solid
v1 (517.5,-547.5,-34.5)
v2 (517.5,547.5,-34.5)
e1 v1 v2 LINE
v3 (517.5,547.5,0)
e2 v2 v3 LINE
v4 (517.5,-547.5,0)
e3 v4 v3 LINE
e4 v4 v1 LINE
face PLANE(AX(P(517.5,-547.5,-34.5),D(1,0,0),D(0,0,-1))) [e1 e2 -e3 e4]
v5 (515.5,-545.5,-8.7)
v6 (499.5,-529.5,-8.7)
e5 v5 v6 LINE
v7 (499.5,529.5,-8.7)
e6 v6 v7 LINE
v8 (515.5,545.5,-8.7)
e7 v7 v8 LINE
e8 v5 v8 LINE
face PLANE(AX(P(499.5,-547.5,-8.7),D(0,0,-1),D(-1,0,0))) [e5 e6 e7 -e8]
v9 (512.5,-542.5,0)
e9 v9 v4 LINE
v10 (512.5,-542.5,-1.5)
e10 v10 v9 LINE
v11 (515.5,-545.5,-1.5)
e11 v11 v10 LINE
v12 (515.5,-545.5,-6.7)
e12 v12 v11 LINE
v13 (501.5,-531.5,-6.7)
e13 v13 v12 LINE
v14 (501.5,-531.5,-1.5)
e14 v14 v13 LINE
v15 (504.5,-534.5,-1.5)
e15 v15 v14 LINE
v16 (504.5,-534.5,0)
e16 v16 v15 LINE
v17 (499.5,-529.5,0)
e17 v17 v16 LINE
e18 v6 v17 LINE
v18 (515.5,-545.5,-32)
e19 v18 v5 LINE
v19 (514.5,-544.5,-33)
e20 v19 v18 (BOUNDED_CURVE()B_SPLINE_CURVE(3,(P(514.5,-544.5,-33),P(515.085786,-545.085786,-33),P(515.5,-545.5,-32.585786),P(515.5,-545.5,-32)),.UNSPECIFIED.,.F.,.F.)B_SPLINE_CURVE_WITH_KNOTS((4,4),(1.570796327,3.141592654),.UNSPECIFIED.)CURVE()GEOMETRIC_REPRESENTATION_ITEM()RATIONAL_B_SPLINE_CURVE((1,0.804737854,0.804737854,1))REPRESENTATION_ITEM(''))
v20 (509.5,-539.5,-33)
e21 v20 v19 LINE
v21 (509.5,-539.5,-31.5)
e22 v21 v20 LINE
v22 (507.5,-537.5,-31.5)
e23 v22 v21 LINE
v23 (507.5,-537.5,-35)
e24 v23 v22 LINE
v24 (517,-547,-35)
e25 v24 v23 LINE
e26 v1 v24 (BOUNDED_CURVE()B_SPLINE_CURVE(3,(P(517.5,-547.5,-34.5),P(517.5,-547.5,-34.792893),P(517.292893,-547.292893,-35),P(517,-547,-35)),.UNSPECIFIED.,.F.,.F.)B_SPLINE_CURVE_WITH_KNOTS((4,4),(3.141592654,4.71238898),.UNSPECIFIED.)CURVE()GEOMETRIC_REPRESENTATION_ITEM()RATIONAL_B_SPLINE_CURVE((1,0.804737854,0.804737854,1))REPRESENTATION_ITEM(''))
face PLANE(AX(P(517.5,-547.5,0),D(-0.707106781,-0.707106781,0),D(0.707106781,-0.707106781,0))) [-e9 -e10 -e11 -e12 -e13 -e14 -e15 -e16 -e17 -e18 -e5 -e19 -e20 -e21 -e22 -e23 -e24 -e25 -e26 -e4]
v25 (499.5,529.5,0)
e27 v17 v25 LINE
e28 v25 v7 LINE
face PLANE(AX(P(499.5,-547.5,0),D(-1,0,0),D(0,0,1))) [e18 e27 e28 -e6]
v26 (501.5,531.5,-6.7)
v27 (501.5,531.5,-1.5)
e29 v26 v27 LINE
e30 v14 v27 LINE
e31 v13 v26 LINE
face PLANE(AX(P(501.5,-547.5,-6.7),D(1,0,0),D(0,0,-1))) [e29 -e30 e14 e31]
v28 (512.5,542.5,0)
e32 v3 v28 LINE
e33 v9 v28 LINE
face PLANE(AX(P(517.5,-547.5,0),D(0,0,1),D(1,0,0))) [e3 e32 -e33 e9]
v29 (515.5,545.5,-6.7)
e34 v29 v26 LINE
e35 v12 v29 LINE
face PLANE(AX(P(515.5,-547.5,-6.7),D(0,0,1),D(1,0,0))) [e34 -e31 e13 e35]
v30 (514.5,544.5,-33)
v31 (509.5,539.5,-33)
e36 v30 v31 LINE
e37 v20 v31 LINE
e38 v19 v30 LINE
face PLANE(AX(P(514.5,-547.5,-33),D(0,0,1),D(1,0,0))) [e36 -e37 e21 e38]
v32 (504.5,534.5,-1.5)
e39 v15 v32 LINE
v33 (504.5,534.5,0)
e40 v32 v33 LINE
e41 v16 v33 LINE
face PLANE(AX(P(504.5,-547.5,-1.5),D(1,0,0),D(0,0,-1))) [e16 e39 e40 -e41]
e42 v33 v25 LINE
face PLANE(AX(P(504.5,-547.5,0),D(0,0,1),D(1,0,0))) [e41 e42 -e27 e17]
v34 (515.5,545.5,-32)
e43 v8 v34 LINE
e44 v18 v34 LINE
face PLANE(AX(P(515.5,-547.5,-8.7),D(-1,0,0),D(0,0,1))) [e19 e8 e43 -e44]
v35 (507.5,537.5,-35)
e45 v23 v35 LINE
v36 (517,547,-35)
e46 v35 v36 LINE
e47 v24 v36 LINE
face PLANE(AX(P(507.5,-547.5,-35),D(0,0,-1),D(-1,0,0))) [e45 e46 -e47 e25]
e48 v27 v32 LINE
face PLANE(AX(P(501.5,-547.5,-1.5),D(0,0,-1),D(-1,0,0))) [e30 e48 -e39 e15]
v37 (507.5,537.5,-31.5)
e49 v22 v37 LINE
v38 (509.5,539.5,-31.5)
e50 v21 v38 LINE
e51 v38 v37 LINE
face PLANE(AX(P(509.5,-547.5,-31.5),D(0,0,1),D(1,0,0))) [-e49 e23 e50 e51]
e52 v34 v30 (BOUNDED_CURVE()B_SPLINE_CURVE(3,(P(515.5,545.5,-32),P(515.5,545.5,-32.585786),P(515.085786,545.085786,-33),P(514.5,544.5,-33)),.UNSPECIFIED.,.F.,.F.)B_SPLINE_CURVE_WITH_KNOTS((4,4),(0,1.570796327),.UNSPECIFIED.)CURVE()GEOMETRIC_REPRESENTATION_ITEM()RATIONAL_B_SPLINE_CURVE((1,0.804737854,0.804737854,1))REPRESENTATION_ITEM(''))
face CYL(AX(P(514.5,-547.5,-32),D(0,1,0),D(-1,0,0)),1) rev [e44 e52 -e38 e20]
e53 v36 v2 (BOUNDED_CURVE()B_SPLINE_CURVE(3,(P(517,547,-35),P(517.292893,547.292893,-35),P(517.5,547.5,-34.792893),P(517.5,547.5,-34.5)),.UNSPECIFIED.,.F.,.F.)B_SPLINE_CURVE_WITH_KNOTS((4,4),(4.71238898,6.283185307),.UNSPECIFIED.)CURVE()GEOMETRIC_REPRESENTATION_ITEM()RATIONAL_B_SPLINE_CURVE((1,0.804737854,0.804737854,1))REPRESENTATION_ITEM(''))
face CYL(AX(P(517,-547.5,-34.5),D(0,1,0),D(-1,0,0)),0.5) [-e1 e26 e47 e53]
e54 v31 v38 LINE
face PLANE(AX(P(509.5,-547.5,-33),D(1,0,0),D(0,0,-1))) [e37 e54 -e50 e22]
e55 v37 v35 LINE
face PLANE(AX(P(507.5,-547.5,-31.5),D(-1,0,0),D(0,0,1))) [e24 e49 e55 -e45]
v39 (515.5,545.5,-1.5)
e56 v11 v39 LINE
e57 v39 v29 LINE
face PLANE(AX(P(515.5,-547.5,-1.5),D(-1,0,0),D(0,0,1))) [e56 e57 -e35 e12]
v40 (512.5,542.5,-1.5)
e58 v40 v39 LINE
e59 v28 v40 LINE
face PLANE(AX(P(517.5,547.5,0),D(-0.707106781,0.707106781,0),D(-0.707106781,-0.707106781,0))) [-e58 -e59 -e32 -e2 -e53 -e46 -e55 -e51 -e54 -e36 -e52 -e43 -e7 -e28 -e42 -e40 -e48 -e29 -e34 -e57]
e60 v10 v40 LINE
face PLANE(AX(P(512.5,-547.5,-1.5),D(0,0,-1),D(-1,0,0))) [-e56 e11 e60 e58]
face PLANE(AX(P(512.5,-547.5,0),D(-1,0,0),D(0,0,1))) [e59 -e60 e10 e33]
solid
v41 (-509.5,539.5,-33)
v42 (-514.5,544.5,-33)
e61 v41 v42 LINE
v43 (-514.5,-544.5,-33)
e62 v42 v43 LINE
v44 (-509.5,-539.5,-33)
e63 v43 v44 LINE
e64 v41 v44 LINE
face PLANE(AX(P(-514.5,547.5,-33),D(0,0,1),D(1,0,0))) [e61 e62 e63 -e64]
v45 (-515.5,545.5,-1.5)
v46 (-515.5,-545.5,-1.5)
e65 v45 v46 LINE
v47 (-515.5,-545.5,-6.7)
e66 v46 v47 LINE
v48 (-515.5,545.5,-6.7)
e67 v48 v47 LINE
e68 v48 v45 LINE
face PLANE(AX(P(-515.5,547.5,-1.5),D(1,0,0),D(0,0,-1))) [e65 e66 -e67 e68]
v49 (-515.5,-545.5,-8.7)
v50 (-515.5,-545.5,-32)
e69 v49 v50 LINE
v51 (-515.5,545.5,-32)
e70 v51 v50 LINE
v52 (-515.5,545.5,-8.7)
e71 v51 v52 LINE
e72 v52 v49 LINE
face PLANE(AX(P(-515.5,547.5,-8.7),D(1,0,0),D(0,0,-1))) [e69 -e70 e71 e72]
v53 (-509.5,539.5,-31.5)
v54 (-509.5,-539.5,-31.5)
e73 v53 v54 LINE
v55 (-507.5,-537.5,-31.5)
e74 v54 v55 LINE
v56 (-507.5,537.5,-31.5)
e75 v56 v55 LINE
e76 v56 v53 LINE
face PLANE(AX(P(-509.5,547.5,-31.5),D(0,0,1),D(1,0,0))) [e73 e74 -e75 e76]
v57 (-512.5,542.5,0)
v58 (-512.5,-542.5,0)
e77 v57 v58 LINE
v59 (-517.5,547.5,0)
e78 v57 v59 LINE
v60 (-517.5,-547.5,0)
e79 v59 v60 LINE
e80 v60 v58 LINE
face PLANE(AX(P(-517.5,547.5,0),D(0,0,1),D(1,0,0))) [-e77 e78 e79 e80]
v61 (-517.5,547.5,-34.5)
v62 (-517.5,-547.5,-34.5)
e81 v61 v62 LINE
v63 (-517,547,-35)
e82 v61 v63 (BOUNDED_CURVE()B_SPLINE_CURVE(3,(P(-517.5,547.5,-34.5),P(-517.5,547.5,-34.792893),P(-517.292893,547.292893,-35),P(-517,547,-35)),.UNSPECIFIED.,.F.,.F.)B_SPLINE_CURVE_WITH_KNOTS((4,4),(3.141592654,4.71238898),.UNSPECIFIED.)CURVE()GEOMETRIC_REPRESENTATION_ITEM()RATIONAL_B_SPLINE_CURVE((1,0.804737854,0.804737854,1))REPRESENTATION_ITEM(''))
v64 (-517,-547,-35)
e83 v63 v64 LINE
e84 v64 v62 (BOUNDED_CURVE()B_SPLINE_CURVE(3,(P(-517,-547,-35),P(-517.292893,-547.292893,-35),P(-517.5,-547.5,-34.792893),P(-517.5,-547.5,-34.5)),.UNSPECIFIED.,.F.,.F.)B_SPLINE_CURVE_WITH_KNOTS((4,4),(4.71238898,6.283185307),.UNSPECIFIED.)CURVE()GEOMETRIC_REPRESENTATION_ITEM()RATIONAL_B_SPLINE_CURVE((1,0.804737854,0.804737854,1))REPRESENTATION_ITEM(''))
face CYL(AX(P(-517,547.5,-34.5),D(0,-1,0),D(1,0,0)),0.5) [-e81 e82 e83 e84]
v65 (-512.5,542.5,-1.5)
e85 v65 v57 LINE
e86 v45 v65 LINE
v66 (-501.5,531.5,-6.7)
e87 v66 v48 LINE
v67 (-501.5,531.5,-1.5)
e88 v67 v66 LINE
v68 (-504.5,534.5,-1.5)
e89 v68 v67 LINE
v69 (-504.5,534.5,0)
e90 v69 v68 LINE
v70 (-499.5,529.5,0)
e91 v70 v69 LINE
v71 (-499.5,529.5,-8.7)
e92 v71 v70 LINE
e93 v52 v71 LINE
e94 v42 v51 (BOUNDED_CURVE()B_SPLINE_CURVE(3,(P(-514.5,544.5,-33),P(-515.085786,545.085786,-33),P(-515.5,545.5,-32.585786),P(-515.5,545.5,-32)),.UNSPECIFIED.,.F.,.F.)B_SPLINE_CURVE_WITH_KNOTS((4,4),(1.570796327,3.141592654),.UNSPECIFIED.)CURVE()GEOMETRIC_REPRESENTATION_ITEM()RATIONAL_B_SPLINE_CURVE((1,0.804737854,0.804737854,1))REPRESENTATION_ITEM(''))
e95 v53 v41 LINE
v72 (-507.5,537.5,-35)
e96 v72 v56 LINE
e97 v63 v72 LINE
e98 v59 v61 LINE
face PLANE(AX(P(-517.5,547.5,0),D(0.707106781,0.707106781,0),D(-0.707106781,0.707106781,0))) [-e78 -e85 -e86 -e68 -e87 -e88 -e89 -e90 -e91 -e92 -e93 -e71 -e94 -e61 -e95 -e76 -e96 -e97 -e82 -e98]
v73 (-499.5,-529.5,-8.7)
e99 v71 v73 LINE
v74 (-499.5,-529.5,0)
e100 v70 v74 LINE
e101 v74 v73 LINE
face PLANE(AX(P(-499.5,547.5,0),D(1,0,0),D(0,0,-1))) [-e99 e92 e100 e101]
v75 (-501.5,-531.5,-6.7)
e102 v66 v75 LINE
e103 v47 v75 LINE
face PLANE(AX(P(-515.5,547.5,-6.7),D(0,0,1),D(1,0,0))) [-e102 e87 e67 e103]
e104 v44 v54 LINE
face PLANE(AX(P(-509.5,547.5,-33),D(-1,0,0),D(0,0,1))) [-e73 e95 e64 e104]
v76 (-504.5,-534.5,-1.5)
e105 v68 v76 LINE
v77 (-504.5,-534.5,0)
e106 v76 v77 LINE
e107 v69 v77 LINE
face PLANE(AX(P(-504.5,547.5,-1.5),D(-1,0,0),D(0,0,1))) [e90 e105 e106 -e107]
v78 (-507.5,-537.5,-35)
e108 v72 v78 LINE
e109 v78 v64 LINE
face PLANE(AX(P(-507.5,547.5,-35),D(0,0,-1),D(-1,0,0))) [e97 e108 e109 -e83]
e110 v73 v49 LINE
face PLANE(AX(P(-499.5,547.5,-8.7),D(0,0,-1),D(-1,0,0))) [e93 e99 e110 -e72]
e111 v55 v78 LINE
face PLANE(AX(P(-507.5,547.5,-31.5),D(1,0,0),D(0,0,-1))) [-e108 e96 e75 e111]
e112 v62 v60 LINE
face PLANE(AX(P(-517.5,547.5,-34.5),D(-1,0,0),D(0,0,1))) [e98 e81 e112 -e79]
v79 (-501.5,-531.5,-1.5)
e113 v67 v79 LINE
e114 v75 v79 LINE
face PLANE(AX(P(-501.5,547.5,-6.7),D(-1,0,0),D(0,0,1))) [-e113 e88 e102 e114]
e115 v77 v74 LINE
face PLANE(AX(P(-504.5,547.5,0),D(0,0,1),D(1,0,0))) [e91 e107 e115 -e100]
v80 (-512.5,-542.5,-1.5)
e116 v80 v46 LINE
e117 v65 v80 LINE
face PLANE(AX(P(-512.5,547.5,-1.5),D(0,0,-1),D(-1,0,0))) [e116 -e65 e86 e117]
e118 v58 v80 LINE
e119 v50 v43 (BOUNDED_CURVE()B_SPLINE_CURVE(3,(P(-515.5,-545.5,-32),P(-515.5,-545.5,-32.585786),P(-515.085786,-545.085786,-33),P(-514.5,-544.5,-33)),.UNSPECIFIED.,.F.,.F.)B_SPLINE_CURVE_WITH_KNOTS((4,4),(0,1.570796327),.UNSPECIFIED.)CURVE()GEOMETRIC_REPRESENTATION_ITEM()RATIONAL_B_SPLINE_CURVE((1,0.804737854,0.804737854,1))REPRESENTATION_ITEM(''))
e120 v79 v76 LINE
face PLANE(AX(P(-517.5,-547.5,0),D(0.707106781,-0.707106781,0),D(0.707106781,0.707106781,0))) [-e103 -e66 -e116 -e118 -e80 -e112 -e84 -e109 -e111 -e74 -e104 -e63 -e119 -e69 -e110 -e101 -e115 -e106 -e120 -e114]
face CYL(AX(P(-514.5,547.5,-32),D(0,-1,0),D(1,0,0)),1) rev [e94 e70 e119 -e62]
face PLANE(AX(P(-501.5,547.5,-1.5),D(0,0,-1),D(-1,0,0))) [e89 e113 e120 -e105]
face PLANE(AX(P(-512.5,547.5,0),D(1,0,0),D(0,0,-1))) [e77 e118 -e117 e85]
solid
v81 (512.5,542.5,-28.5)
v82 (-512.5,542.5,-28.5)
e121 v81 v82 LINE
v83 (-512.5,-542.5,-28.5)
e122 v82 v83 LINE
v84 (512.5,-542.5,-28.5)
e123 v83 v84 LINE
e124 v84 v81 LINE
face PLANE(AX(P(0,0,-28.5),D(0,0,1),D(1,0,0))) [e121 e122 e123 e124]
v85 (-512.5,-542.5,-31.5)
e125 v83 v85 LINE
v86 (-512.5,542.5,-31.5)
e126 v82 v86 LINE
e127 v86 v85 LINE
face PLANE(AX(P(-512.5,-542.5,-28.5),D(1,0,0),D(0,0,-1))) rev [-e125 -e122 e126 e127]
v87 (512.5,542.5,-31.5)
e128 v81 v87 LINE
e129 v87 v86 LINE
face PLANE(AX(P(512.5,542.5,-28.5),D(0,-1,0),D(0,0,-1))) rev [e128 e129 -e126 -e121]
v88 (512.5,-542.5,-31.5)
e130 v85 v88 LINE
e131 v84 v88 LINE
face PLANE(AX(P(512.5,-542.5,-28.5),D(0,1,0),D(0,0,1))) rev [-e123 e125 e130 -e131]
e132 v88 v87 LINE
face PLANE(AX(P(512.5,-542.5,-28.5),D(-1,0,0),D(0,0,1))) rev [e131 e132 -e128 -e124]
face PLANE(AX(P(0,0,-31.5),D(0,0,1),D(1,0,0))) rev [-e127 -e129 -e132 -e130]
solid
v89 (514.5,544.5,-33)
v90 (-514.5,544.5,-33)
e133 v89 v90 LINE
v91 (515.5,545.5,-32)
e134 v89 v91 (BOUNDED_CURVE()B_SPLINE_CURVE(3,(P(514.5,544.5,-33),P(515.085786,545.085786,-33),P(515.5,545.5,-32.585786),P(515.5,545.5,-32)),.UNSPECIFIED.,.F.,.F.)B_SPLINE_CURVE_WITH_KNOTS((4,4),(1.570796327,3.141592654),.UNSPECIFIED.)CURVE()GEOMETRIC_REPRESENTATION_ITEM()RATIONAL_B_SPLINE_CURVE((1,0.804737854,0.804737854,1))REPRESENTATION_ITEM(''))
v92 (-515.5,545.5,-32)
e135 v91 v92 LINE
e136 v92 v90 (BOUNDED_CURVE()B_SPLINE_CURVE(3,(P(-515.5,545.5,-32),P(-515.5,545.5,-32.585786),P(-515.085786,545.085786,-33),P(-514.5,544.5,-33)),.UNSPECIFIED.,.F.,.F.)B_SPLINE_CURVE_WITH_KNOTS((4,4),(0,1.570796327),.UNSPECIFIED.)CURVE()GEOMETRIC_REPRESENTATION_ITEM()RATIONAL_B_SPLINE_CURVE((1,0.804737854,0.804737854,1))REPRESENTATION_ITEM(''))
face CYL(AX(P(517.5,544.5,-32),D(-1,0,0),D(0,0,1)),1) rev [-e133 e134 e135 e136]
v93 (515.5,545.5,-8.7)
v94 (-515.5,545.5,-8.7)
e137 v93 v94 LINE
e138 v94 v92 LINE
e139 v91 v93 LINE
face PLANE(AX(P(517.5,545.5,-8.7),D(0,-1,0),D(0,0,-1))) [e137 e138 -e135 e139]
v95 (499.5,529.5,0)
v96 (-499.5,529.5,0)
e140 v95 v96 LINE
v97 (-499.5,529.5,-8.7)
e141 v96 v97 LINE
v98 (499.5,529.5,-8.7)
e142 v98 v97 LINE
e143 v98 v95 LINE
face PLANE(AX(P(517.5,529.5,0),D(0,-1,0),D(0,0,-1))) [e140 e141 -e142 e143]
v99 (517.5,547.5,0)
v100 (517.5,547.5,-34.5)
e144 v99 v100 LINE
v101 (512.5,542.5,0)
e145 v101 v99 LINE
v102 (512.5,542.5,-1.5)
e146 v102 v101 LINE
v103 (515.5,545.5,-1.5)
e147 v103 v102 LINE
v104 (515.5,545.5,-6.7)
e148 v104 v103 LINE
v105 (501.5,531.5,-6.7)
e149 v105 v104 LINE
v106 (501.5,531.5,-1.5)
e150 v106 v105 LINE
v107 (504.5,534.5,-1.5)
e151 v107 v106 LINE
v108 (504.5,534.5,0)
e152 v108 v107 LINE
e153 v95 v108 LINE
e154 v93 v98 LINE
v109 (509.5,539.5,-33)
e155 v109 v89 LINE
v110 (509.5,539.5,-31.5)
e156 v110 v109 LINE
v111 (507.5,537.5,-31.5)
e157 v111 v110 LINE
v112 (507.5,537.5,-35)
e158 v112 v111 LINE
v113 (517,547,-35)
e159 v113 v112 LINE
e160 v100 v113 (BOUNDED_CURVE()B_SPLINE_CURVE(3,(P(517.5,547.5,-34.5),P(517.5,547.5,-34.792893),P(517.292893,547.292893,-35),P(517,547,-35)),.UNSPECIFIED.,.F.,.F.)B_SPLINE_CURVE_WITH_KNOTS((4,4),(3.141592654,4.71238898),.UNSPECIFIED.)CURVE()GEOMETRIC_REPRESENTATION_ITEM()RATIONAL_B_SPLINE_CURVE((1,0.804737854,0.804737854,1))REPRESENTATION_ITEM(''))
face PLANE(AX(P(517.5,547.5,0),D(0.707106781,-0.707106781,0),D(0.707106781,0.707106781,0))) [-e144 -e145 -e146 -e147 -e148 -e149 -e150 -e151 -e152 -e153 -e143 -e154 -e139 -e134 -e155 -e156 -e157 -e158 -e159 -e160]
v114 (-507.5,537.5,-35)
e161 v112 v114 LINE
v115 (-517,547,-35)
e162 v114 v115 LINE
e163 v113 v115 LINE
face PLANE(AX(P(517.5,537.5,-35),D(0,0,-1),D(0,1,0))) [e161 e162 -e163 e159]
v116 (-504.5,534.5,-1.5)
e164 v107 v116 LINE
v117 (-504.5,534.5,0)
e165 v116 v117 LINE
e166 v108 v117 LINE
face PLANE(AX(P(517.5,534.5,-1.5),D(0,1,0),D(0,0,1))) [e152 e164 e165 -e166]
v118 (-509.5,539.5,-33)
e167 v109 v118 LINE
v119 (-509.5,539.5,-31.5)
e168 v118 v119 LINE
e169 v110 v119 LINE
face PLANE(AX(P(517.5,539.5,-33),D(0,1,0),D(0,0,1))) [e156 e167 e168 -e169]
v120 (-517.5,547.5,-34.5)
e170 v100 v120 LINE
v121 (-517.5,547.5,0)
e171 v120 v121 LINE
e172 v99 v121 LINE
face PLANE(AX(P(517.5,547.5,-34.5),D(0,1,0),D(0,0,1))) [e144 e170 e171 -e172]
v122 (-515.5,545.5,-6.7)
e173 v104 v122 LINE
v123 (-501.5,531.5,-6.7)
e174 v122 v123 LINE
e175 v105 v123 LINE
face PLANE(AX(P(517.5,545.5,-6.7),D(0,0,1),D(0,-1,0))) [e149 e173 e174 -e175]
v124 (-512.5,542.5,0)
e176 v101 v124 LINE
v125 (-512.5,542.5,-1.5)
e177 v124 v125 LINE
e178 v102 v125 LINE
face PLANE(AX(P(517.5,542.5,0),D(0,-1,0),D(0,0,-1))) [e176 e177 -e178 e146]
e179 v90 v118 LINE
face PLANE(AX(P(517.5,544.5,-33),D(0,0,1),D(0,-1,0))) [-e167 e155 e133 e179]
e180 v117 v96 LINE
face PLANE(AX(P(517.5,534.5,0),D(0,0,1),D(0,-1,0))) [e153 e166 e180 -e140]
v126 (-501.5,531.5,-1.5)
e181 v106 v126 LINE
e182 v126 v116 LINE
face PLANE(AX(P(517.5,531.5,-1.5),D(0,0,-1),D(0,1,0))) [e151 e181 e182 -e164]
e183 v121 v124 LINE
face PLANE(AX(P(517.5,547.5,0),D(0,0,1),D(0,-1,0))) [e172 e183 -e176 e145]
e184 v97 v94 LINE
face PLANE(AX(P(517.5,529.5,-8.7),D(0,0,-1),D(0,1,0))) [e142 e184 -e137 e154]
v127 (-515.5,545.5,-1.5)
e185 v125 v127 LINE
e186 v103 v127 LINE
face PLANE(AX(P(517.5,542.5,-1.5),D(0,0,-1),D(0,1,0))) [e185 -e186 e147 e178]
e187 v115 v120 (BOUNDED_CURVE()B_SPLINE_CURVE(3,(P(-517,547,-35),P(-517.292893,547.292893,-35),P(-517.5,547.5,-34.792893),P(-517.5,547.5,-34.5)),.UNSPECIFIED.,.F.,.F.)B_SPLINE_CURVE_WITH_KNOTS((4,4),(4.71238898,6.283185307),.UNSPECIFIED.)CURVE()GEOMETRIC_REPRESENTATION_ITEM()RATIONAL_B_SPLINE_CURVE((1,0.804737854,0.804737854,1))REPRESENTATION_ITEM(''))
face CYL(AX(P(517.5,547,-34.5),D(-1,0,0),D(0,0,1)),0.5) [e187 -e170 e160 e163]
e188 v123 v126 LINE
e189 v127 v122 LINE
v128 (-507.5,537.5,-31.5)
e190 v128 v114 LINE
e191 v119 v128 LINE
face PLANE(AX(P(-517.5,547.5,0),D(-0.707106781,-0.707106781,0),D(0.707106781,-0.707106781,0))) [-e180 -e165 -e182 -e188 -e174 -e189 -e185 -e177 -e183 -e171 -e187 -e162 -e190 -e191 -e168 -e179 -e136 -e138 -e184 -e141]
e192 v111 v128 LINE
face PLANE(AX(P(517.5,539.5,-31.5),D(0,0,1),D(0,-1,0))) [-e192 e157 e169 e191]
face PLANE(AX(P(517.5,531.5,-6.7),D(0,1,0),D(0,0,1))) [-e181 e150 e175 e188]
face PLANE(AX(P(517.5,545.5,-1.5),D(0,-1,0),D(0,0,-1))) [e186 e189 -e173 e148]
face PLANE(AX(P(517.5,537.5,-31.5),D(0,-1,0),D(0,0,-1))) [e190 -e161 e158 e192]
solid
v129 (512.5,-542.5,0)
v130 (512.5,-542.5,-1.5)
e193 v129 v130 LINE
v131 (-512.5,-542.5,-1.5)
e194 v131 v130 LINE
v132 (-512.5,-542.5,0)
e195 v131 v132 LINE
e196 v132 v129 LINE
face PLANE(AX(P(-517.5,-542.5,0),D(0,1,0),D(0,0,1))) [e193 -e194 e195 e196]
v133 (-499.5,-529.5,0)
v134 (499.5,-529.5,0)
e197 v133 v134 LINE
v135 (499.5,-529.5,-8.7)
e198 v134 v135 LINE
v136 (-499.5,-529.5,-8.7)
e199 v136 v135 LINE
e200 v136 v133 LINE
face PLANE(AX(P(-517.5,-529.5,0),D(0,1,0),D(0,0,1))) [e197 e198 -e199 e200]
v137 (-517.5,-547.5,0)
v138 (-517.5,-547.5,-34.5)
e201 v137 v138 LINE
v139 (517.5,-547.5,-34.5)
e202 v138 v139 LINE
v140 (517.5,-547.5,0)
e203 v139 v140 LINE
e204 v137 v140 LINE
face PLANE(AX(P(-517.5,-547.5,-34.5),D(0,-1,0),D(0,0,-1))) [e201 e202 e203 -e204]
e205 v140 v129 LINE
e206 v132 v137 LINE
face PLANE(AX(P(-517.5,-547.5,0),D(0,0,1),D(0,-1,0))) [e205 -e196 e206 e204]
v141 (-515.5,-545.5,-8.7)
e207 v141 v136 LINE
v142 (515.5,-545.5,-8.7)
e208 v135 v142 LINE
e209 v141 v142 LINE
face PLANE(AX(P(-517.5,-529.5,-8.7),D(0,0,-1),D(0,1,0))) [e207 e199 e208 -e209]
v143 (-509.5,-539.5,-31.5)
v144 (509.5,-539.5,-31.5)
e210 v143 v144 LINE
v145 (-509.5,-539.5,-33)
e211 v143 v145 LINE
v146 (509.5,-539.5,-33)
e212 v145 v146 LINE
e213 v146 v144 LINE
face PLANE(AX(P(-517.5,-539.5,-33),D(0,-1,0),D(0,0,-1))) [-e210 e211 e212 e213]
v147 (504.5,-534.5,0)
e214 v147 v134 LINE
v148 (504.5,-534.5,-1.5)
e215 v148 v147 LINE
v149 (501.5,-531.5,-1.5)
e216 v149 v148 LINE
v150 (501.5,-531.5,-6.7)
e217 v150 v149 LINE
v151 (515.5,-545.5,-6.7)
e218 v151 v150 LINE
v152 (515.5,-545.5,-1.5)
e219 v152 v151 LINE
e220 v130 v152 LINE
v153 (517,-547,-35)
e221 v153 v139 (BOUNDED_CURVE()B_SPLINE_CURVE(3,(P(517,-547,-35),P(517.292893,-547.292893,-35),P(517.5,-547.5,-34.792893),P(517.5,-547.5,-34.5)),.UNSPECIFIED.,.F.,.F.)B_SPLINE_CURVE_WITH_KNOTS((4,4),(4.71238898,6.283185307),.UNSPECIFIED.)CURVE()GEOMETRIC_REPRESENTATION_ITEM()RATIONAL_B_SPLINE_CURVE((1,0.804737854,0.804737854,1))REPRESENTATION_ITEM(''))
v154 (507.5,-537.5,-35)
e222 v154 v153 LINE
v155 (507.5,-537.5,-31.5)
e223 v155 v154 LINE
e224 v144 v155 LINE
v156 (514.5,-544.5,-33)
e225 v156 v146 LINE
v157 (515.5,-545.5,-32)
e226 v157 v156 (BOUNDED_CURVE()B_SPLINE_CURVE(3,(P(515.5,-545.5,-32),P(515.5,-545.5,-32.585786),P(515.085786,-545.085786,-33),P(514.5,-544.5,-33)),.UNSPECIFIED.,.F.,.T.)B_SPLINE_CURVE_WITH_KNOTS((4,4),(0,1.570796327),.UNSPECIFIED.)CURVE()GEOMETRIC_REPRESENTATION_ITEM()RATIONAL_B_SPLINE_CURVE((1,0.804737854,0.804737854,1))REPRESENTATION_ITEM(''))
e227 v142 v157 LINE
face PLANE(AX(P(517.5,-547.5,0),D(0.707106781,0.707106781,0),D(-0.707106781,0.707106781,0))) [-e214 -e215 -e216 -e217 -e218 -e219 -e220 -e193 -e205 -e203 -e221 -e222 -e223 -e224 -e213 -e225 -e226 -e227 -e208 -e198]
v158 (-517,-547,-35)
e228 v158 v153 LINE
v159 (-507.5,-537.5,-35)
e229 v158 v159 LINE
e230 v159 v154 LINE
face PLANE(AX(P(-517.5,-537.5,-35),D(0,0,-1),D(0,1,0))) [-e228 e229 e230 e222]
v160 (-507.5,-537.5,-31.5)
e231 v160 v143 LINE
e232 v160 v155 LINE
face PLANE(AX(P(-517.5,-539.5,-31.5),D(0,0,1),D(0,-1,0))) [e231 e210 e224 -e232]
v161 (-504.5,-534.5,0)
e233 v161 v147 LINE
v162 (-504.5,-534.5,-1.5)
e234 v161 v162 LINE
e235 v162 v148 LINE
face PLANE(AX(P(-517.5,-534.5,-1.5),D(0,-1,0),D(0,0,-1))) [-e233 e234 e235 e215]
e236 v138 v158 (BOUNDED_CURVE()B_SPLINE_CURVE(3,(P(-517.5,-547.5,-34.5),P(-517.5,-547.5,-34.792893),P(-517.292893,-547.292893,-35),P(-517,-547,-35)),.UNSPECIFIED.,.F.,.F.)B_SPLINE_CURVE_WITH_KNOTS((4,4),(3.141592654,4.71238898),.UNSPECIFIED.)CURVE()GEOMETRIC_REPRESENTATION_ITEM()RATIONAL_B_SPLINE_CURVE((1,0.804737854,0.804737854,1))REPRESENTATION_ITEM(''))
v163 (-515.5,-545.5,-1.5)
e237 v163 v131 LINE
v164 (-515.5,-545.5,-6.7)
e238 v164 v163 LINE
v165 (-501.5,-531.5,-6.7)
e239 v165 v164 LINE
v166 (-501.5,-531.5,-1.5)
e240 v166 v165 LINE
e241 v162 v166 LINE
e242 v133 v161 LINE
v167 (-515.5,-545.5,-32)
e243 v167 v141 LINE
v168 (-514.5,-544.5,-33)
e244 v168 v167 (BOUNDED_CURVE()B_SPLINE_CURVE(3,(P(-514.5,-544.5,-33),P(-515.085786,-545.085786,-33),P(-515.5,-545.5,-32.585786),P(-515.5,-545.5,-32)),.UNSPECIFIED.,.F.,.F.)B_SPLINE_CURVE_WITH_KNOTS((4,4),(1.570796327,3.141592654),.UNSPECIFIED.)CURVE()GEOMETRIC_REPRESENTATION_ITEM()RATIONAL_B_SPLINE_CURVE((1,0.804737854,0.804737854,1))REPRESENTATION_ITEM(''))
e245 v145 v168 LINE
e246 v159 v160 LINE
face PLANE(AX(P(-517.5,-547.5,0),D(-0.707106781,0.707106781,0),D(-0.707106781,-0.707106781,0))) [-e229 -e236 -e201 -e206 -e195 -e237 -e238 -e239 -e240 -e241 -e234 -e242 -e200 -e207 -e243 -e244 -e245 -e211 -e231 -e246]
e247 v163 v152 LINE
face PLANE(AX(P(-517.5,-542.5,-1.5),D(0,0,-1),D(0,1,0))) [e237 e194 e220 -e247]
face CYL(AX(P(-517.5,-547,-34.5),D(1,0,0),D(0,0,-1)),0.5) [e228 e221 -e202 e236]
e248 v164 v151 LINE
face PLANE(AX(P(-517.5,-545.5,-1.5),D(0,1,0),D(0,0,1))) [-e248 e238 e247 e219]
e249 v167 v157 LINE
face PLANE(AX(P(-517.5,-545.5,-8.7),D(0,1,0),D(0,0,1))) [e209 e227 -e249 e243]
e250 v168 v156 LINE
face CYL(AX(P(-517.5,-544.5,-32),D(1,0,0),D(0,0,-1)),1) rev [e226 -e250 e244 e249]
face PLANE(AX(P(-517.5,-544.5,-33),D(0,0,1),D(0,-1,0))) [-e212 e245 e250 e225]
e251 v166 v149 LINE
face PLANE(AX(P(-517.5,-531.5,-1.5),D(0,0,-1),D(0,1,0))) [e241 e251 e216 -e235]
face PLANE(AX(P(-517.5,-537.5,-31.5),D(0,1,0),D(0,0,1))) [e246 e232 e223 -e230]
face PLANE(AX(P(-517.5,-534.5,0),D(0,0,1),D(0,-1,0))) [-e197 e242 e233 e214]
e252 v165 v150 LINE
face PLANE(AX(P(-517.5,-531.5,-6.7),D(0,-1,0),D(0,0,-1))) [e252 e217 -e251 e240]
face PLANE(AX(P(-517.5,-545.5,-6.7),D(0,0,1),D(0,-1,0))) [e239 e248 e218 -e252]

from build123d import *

# Parameters (mm, degrees)
MEMBER_1_DEPTH      = 40.357337308
MEMBER_1_DEPTH_BACK = 1075.357337308
MEMBER_1_2_DEPTH    = 1175.714674617
MEMBER_1_3_DEPTH    = 1115.714674617
MEMBER_1_4_DEPTH    = 1175.714674617
SKETCH_12_W         = 1025
SKETCH_12_H         = 1085
EXTRUDE_1_DEPTH     = 3


with BuildPart() as part:
    # 草图11 → Member 1 (new, two sides: drawn at the far end of the back side and taken through both)
    with BuildSketch(Plane(origin=(-517.5, 547.5, 0), x_dir=(0, -1, 0), z_dir=(-1, 0, 0)).offset(-MEMBER_1_DEPTH_BACK)):
        with BuildLine():
            Line((13, -1.5), (13, 0))
            Line((13, 0), (18, 0))
            Line((18, 0), (18, -8.7))
            Line((18, -8.7), (2, -8.7))
            Line((2, -8.7), (2, -32))
            ThreePointArc((2, -32), (2.292893219, -32.707106781), (3, -33))
            Line((3, -33), (8, -33))
            Line((8, -33), (8, -31.5))
            Line((8, -31.5), (10, -31.5))
            Line((10, -31.5), (10, -35))
            Line((10, -35), (0.5, -35))
            ThreePointArc((0.5, -35), (0.146446609, -34.853553391), (0, -34.5))
            Line((0, -34.5), (0, 0))
            Line((0, 0), (5, 0))
            Line((5, 0), (5, -1.5))
            Line((5, -1.5), (2, -1.5))
            Line((2, -1.5), (2, -6.7))
            Line((2, -6.7), (16, -6.7))
            Line((16, -6.7), (16, -1.5))
            Line((16, -1.5), (13, -1.5))
        make_face()
    extrude(amount=MEMBER_1_DEPTH + MEMBER_1_DEPTH_BACK)

    # Member 1 mitre 1
    split(bisect_by=Plane(origin=(-517.5, 547.5, 0), x_dir=(-0.707106781, 0.707106781, 0), z_dir=(0.707106781, 0.707106781, 0)), keep=Keep.TOP)

    # Member 1 mitre 2
    split(bisect_by=Plane(origin=(517.5, 547.5, 0), x_dir=(-0.707106781, -0.707106781, 0), z_dir=(-0.707106781, 0.707106781, 0)), keep=Keep.TOP)


with BuildPart() as body_2:
    # 草图11 on segment 2 (carried to segment 2) → Member 1 2 (new body)
    with BuildSketch(Plane(origin=(517.5, -587.857337308, 0), x_dir=(-1, 0, 0), z_dir=(0, 1, 0))):
        with BuildLine():
            Line((13, -1.5), (13, 0))
            Line((13, 0), (18, 0))
            Line((18, 0), (18, -8.7))
            Line((18, -8.7), (2, -8.7))
            Line((2, -8.7), (2, -32))
            ThreePointArc((2, -32), (2.292893219, -32.707106781), (3, -33))
            Line((3, -33), (8, -33))
            Line((8, -33), (8, -31.5))
            Line((8, -31.5), (10, -31.5))
            Line((10, -31.5), (10, -35))
            Line((10, -35), (0.5, -35))
            ThreePointArc((0.5, -35), (0.146446609, -34.853553391), (0, -34.5))
            Line((0, -34.5), (0, 0))
            Line((0, 0), (5, 0))
            Line((5, 0), (5, -1.5))
            Line((5, -1.5), (2, -1.5))
            Line((2, -1.5), (2, -6.7))
            Line((2, -6.7), (16, -6.7))
            Line((16, -6.7), (16, -1.5))
            Line((16, -1.5), (13, -1.5))
        make_face()
    extrude(amount=MEMBER_1_2_DEPTH)

    # Member 1 2 mitre 1
    split(bisect_by=Plane(origin=(517.5, 547.5, 0), x_dir=(0.707106781, 0.707106781, 0), z_dir=(0.707106781, -0.707106781, 0)), keep=Keep.TOP)

    # Member 1 2 mitre 2
    split(bisect_by=Plane(origin=(517.5, -547.5, 0), x_dir=(-0.707106781, 0.707106781, 0), z_dir=(0.707106781, 0.707106781, 0)), keep=Keep.TOP)


with BuildPart() as body_3:
    # 草图11 on segment 3 (carried to segment 3) → Member 1 3 (new body)
    with BuildSketch(Plane(origin=(-557.857337308, -547.5, 0), x_dir=(0, 1, 0), z_dir=(1, 0, 0))):
        with BuildLine():
            Line((13, -1.5), (13, 0))
            Line((13, 0), (18, 0))
            Line((18, 0), (18, -8.7))
            Line((18, -8.7), (2, -8.7))
            Line((2, -8.7), (2, -32))
            ThreePointArc((2, -32), (2.292893219, -32.707106781), (3, -33))
            Line((3, -33), (8, -33))
            Line((8, -33), (8, -31.5))
            Line((8, -31.5), (10, -31.5))
            Line((10, -31.5), (10, -35))
            Line((10, -35), (0.5, -35))
            ThreePointArc((0.5, -35), (0.146446609, -34.853553391), (0, -34.5))
            Line((0, -34.5), (0, 0))
            Line((0, 0), (5, 0))
            Line((5, 0), (5, -1.5))
            Line((5, -1.5), (2, -1.5))
            Line((2, -1.5), (2, -6.7))
            Line((2, -6.7), (16, -6.7))
            Line((16, -6.7), (16, -1.5))
            Line((16, -1.5), (13, -1.5))
        make_face()
    extrude(amount=MEMBER_1_3_DEPTH)

    # Member 1 3 mitre 1
    split(bisect_by=Plane(origin=(-517.5, -547.5, 0), x_dir=(0.707106781, 0.707106781, 0), z_dir=(0.707106781, -0.707106781, 0)), keep=Keep.TOP)

    # Member 1 3 mitre 2
    split(bisect_by=Plane(origin=(517.5, -547.5, 0), x_dir=(0.707106781, -0.707106781, 0), z_dir=(-0.707106781, -0.707106781, 0)), keep=Keep.TOP)


with BuildPart() as body_4:
    # 草图11 on segment 4 (carried to segment 4) → Member 1 4 (new body)
    with BuildSketch(Plane(origin=(-517.5, 587.857337308, 0), x_dir=(1, 0, 0), z_dir=(0, -1, 0))):
        with BuildLine():
            Line((13, -1.5), (13, 0))
            Line((13, 0), (18, 0))
            Line((18, 0), (18, -8.7))
            Line((18, -8.7), (2, -8.7))
            Line((2, -8.7), (2, -32))
            ThreePointArc((2, -32), (2.292893219, -32.707106781), (3, -33))
            Line((3, -33), (8, -33))
            Line((8, -33), (8, -31.5))
            Line((8, -31.5), (10, -31.5))
            Line((10, -31.5), (10, -35))
            Line((10, -35), (0.5, -35))
            ThreePointArc((0.5, -35), (0.146446609, -34.853553391), (0, -34.5))
            Line((0, -34.5), (0, 0))
            Line((0, 0), (5, 0))
            Line((5, 0), (5, -1.5))
            Line((5, -1.5), (2, -1.5))
            Line((2, -1.5), (2, -6.7))
            Line((2, -6.7), (16, -6.7))
            Line((16, -6.7), (16, -1.5))
            Line((16, -1.5), (13, -1.5))
        make_face()
    extrude(amount=MEMBER_1_4_DEPTH)

    # Member 1 4 mitre 1
    split(bisect_by=Plane(origin=(-517.5, 547.5, 0), x_dir=(0.707106781, -0.707106781, 0), z_dir=(-0.707106781, -0.707106781, 0)), keep=Keep.TOP)

    # Member 1 4 mitre 2
    split(bisect_by=Plane(origin=(-517.5, -547.5, 0), x_dir=(-0.707106781, -0.707106781, 0), z_dir=(-0.707106781, 0.707106781, 0)), keep=Keep.TOP)


with BuildPart() as body_5:
    # 草图12 → 凸台-拉伸1 (new body)
    with BuildSketch(Plane.XY.offset(-31.5)):
        Rectangle(SKETCH_12_W, SKETCH_12_H)
    extrude(amount=EXTRUDE_1_DEPTH)


solid = Compound([part.part, body_2.part, body_3.part, body_4.part, body_5.part])
